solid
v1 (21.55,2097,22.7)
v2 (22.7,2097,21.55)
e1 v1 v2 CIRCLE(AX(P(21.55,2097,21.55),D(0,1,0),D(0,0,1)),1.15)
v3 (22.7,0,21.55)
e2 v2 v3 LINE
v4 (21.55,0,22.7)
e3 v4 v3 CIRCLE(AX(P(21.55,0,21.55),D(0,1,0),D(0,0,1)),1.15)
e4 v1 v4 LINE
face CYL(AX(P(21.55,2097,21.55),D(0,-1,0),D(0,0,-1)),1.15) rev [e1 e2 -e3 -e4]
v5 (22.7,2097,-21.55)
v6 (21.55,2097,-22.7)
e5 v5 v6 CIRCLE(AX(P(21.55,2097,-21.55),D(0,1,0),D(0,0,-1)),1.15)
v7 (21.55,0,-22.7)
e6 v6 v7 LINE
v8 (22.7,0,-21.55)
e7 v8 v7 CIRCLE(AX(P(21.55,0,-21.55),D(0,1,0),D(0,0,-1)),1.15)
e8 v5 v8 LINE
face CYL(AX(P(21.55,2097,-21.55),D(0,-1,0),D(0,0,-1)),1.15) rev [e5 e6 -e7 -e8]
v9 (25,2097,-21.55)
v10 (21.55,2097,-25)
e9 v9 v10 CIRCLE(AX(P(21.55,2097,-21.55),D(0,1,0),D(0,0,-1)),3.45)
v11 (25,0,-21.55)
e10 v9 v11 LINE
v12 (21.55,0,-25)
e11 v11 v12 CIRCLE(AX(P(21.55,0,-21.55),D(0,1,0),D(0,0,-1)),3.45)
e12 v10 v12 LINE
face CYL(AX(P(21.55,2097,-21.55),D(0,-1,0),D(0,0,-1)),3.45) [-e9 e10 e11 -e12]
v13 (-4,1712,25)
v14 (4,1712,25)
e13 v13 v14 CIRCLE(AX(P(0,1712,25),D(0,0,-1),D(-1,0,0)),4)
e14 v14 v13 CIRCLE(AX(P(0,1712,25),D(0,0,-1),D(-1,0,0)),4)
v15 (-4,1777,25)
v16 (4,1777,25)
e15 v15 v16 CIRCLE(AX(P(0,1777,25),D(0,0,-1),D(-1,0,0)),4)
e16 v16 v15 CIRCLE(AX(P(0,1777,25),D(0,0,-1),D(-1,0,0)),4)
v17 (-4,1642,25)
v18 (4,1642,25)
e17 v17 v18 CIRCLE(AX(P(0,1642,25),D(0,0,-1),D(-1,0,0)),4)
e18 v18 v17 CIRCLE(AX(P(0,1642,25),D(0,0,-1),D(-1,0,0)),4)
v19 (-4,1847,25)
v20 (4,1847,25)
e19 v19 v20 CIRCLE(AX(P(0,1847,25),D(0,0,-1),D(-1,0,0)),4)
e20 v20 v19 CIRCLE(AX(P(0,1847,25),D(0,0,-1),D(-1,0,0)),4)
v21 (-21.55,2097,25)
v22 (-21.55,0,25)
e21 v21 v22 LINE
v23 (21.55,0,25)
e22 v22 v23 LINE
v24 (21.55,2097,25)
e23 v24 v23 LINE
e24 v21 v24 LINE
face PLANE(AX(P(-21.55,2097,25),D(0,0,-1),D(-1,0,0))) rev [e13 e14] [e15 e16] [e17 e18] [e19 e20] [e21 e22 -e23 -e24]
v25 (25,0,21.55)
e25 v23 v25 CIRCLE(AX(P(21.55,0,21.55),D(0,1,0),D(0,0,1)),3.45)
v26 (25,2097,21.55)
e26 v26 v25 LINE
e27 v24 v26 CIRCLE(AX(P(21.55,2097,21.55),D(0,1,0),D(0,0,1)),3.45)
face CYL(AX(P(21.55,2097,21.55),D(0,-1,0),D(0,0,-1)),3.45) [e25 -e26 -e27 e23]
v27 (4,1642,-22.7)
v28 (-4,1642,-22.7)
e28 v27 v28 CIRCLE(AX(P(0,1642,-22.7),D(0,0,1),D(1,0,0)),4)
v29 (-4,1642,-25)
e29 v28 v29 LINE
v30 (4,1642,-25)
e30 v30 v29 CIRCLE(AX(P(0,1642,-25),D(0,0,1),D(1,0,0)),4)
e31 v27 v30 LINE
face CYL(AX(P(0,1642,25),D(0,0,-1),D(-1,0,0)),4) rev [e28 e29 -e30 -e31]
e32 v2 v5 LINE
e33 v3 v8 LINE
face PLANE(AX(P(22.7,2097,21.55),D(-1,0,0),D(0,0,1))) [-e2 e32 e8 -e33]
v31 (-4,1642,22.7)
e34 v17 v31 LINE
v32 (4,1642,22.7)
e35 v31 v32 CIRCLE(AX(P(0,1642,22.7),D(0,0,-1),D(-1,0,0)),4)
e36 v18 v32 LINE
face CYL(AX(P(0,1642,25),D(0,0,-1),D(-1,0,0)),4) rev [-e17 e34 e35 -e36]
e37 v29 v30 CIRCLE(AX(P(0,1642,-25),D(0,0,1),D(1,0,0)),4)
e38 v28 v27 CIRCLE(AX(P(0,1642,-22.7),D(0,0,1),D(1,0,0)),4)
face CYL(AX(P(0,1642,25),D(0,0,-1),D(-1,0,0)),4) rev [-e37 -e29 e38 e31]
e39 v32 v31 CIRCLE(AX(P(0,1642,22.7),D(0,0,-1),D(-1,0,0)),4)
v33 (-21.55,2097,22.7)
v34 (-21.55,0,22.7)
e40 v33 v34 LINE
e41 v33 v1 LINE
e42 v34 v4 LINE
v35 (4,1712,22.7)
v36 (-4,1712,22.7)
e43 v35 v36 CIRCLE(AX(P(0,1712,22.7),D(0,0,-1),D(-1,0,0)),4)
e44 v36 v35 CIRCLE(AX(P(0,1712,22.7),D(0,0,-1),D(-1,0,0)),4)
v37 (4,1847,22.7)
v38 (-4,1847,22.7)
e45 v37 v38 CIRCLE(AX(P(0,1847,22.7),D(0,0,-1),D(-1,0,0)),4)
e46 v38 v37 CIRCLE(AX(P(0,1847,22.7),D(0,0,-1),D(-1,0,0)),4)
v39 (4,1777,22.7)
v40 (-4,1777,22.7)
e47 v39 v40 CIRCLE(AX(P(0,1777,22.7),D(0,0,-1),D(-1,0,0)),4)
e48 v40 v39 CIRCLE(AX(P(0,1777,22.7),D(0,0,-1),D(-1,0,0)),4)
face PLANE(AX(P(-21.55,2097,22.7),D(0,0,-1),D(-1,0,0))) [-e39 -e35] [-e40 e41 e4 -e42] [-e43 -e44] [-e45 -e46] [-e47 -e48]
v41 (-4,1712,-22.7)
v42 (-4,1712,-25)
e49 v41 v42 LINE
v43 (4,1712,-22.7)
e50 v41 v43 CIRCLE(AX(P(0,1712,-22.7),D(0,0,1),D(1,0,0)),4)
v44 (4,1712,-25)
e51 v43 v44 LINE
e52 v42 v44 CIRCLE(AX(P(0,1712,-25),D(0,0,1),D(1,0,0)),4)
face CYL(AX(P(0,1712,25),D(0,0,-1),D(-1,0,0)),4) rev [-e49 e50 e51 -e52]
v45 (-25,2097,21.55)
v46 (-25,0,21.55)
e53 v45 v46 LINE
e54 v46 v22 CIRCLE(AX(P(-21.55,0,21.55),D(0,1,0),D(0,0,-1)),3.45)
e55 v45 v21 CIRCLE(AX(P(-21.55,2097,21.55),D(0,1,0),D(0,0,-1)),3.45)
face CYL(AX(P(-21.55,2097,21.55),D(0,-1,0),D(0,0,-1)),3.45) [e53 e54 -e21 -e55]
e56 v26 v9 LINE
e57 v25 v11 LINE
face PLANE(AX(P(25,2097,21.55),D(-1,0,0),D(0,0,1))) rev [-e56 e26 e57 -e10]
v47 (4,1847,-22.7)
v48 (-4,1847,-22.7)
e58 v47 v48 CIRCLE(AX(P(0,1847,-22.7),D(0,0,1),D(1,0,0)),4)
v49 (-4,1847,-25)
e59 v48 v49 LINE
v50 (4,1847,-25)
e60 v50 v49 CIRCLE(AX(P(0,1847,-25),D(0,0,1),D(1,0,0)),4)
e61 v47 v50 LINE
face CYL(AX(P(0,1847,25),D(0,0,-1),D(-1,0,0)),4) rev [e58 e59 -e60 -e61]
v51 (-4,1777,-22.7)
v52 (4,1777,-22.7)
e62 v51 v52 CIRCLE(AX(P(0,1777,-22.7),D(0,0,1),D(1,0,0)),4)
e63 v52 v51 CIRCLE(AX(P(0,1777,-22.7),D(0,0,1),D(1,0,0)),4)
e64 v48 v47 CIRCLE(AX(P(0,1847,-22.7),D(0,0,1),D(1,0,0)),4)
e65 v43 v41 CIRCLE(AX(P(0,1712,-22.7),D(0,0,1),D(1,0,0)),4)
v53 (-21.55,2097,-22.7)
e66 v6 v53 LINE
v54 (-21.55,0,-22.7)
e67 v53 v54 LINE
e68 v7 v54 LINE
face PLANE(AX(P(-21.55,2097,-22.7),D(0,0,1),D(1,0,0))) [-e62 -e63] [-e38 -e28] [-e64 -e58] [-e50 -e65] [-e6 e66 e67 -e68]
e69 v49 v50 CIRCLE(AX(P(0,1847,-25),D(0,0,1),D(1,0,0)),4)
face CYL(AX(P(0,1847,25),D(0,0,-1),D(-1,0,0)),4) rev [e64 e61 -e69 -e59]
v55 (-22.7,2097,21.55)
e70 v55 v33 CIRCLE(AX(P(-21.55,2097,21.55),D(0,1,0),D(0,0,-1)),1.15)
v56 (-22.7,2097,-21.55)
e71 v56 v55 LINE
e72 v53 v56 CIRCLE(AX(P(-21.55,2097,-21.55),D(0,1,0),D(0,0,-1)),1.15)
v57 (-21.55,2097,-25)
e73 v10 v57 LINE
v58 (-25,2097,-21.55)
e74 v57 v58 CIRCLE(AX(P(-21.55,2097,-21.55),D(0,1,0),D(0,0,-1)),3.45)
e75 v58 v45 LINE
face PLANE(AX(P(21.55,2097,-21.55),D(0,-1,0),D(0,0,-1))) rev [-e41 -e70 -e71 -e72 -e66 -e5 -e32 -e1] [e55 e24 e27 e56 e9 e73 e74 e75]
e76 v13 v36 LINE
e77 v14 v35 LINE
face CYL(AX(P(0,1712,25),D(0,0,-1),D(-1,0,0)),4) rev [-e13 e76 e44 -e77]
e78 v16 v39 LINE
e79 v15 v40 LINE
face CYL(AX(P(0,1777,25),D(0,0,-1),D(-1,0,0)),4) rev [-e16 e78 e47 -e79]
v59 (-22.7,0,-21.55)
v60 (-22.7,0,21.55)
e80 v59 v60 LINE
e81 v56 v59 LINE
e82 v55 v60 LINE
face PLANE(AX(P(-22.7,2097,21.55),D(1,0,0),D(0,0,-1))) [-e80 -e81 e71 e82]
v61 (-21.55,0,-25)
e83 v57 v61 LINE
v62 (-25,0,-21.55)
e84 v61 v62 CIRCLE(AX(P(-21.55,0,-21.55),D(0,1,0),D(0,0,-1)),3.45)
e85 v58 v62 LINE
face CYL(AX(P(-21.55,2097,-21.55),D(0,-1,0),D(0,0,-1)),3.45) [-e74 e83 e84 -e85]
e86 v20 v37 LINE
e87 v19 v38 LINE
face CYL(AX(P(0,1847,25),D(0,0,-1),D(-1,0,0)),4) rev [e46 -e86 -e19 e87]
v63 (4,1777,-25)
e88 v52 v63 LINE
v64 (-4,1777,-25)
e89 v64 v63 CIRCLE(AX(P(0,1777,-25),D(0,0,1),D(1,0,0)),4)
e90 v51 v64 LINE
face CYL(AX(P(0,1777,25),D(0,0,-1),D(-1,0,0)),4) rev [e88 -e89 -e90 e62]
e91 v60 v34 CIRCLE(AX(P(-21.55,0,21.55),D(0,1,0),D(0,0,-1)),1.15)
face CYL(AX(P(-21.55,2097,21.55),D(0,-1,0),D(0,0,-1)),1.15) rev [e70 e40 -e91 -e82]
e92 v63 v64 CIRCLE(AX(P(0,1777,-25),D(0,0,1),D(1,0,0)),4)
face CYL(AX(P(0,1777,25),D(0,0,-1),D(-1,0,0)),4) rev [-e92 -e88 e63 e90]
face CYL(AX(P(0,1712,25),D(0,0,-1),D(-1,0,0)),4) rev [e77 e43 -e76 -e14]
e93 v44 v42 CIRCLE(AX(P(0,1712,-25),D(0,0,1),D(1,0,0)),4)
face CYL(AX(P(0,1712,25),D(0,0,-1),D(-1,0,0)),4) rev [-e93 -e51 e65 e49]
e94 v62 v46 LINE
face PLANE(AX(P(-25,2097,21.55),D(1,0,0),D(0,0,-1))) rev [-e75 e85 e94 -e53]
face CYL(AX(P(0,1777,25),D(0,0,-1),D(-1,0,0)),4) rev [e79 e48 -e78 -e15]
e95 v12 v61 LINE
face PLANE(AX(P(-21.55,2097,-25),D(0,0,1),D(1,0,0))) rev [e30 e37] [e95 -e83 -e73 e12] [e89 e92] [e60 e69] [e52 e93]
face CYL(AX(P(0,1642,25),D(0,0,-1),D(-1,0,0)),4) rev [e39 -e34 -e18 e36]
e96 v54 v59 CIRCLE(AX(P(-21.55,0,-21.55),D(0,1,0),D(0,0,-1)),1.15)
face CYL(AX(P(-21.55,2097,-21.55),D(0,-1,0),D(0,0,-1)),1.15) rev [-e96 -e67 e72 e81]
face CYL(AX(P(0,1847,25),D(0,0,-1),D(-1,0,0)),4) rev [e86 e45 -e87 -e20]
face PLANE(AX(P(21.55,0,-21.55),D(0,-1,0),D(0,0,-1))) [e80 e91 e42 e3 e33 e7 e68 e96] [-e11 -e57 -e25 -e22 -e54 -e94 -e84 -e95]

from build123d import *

# Parameters (mm, degrees)
BOSS_EXTRUDE1_DEPTH     = 2097
CUT_EXTRUDE1_DEPTH      = 2098.744979734
CUT_EXTRUDE1_DEPTH_BACK = 2098.744979734
SKETCH2_R               = 4


with BuildPart() as part:
    # Sketch1 → Boss-Extrude1 (new body)
    with BuildSketch(Plane(origin=(0, 0, 0), x_dir=(1, 0, 0), z_dir=(0, 1, 0))):
        with BuildLine():
            Line((-21.55, -25), (21.55, -25))
            ThreePointArc((21.55, -25), (23.989518395, -23.989518395), (25, -21.55))
            Line((25, -21.55), (25, 21.55))
            ThreePointArc((25, 21.55), (23.989518395, 23.989518395), (21.55, 25))
            Line((21.55, 25), (-21.55, 25))
            ThreePointArc((-21.55, 25), (-23.989518395, 23.989518395), (-25, 21.55))
            Line((-25, 21.55), (-25, -21.55))
            ThreePointArc((-25, -21.55), (-23.989518395, -23.989518395), (-21.55, -25))
        make_face()
        with BuildLine():
            Line((-21.55, -22.7), (21.55, -22.7))
            ThreePointArc((21.55, -22.7), (22.363172798, -22.363172798), (22.7, -21.55))
            Line((22.7, -21.55), (22.7, 21.55))
            ThreePointArc((22.7, 21.55), (22.363172798, 22.363172798), (21.55, 22.7))
            Line((21.55, 22.7), (-21.55, 22.7))
            ThreePointArc((-21.55, 22.7), (-22.363172798, 22.363172798), (-22.7, 21.55))
            Line((-22.7, 21.55), (-22.7, -21.55))
            ThreePointArc((-22.7, -21.55), (-22.363172798, -22.363172798), (-21.55, -22.7))
        make_face(mode=Mode.SUBTRACT)
    extrude(amount=BOSS_EXTRUDE1_DEPTH)

    # Sketch2 → Cut-Extrude1 (cut, two sides: drawn at the far end of the back side and taken through both)
    with BuildSketch(Plane(origin=(0, 0, -25), x_dir=(-1, 0, 0), z_dir=(0, 0, -1)).offset(-CUT_EXTRUDE1_DEPTH_BACK)):
        with Locations(Location((0, 1847, 0), (0, 0, 180))):
            Circle(SKETCH2_R)
        with Locations(Location((0, 1777, 0), (0, 0, 180))):
            Circle(SKETCH2_R)
        with Locations(Location((0, 1712, 0), (0, 0, 180))):
            Circle(SKETCH2_R)
        with Locations(Location((0, 1642, 0), (0, 0, 180))):
            Circle(SKETCH2_R)
    extrude(amount=CUT_EXTRUDE1_DEPTH + CUT_EXTRUDE1_DEPTH_BACK, mode=Mode.SUBTRACT)


solid = part.part
